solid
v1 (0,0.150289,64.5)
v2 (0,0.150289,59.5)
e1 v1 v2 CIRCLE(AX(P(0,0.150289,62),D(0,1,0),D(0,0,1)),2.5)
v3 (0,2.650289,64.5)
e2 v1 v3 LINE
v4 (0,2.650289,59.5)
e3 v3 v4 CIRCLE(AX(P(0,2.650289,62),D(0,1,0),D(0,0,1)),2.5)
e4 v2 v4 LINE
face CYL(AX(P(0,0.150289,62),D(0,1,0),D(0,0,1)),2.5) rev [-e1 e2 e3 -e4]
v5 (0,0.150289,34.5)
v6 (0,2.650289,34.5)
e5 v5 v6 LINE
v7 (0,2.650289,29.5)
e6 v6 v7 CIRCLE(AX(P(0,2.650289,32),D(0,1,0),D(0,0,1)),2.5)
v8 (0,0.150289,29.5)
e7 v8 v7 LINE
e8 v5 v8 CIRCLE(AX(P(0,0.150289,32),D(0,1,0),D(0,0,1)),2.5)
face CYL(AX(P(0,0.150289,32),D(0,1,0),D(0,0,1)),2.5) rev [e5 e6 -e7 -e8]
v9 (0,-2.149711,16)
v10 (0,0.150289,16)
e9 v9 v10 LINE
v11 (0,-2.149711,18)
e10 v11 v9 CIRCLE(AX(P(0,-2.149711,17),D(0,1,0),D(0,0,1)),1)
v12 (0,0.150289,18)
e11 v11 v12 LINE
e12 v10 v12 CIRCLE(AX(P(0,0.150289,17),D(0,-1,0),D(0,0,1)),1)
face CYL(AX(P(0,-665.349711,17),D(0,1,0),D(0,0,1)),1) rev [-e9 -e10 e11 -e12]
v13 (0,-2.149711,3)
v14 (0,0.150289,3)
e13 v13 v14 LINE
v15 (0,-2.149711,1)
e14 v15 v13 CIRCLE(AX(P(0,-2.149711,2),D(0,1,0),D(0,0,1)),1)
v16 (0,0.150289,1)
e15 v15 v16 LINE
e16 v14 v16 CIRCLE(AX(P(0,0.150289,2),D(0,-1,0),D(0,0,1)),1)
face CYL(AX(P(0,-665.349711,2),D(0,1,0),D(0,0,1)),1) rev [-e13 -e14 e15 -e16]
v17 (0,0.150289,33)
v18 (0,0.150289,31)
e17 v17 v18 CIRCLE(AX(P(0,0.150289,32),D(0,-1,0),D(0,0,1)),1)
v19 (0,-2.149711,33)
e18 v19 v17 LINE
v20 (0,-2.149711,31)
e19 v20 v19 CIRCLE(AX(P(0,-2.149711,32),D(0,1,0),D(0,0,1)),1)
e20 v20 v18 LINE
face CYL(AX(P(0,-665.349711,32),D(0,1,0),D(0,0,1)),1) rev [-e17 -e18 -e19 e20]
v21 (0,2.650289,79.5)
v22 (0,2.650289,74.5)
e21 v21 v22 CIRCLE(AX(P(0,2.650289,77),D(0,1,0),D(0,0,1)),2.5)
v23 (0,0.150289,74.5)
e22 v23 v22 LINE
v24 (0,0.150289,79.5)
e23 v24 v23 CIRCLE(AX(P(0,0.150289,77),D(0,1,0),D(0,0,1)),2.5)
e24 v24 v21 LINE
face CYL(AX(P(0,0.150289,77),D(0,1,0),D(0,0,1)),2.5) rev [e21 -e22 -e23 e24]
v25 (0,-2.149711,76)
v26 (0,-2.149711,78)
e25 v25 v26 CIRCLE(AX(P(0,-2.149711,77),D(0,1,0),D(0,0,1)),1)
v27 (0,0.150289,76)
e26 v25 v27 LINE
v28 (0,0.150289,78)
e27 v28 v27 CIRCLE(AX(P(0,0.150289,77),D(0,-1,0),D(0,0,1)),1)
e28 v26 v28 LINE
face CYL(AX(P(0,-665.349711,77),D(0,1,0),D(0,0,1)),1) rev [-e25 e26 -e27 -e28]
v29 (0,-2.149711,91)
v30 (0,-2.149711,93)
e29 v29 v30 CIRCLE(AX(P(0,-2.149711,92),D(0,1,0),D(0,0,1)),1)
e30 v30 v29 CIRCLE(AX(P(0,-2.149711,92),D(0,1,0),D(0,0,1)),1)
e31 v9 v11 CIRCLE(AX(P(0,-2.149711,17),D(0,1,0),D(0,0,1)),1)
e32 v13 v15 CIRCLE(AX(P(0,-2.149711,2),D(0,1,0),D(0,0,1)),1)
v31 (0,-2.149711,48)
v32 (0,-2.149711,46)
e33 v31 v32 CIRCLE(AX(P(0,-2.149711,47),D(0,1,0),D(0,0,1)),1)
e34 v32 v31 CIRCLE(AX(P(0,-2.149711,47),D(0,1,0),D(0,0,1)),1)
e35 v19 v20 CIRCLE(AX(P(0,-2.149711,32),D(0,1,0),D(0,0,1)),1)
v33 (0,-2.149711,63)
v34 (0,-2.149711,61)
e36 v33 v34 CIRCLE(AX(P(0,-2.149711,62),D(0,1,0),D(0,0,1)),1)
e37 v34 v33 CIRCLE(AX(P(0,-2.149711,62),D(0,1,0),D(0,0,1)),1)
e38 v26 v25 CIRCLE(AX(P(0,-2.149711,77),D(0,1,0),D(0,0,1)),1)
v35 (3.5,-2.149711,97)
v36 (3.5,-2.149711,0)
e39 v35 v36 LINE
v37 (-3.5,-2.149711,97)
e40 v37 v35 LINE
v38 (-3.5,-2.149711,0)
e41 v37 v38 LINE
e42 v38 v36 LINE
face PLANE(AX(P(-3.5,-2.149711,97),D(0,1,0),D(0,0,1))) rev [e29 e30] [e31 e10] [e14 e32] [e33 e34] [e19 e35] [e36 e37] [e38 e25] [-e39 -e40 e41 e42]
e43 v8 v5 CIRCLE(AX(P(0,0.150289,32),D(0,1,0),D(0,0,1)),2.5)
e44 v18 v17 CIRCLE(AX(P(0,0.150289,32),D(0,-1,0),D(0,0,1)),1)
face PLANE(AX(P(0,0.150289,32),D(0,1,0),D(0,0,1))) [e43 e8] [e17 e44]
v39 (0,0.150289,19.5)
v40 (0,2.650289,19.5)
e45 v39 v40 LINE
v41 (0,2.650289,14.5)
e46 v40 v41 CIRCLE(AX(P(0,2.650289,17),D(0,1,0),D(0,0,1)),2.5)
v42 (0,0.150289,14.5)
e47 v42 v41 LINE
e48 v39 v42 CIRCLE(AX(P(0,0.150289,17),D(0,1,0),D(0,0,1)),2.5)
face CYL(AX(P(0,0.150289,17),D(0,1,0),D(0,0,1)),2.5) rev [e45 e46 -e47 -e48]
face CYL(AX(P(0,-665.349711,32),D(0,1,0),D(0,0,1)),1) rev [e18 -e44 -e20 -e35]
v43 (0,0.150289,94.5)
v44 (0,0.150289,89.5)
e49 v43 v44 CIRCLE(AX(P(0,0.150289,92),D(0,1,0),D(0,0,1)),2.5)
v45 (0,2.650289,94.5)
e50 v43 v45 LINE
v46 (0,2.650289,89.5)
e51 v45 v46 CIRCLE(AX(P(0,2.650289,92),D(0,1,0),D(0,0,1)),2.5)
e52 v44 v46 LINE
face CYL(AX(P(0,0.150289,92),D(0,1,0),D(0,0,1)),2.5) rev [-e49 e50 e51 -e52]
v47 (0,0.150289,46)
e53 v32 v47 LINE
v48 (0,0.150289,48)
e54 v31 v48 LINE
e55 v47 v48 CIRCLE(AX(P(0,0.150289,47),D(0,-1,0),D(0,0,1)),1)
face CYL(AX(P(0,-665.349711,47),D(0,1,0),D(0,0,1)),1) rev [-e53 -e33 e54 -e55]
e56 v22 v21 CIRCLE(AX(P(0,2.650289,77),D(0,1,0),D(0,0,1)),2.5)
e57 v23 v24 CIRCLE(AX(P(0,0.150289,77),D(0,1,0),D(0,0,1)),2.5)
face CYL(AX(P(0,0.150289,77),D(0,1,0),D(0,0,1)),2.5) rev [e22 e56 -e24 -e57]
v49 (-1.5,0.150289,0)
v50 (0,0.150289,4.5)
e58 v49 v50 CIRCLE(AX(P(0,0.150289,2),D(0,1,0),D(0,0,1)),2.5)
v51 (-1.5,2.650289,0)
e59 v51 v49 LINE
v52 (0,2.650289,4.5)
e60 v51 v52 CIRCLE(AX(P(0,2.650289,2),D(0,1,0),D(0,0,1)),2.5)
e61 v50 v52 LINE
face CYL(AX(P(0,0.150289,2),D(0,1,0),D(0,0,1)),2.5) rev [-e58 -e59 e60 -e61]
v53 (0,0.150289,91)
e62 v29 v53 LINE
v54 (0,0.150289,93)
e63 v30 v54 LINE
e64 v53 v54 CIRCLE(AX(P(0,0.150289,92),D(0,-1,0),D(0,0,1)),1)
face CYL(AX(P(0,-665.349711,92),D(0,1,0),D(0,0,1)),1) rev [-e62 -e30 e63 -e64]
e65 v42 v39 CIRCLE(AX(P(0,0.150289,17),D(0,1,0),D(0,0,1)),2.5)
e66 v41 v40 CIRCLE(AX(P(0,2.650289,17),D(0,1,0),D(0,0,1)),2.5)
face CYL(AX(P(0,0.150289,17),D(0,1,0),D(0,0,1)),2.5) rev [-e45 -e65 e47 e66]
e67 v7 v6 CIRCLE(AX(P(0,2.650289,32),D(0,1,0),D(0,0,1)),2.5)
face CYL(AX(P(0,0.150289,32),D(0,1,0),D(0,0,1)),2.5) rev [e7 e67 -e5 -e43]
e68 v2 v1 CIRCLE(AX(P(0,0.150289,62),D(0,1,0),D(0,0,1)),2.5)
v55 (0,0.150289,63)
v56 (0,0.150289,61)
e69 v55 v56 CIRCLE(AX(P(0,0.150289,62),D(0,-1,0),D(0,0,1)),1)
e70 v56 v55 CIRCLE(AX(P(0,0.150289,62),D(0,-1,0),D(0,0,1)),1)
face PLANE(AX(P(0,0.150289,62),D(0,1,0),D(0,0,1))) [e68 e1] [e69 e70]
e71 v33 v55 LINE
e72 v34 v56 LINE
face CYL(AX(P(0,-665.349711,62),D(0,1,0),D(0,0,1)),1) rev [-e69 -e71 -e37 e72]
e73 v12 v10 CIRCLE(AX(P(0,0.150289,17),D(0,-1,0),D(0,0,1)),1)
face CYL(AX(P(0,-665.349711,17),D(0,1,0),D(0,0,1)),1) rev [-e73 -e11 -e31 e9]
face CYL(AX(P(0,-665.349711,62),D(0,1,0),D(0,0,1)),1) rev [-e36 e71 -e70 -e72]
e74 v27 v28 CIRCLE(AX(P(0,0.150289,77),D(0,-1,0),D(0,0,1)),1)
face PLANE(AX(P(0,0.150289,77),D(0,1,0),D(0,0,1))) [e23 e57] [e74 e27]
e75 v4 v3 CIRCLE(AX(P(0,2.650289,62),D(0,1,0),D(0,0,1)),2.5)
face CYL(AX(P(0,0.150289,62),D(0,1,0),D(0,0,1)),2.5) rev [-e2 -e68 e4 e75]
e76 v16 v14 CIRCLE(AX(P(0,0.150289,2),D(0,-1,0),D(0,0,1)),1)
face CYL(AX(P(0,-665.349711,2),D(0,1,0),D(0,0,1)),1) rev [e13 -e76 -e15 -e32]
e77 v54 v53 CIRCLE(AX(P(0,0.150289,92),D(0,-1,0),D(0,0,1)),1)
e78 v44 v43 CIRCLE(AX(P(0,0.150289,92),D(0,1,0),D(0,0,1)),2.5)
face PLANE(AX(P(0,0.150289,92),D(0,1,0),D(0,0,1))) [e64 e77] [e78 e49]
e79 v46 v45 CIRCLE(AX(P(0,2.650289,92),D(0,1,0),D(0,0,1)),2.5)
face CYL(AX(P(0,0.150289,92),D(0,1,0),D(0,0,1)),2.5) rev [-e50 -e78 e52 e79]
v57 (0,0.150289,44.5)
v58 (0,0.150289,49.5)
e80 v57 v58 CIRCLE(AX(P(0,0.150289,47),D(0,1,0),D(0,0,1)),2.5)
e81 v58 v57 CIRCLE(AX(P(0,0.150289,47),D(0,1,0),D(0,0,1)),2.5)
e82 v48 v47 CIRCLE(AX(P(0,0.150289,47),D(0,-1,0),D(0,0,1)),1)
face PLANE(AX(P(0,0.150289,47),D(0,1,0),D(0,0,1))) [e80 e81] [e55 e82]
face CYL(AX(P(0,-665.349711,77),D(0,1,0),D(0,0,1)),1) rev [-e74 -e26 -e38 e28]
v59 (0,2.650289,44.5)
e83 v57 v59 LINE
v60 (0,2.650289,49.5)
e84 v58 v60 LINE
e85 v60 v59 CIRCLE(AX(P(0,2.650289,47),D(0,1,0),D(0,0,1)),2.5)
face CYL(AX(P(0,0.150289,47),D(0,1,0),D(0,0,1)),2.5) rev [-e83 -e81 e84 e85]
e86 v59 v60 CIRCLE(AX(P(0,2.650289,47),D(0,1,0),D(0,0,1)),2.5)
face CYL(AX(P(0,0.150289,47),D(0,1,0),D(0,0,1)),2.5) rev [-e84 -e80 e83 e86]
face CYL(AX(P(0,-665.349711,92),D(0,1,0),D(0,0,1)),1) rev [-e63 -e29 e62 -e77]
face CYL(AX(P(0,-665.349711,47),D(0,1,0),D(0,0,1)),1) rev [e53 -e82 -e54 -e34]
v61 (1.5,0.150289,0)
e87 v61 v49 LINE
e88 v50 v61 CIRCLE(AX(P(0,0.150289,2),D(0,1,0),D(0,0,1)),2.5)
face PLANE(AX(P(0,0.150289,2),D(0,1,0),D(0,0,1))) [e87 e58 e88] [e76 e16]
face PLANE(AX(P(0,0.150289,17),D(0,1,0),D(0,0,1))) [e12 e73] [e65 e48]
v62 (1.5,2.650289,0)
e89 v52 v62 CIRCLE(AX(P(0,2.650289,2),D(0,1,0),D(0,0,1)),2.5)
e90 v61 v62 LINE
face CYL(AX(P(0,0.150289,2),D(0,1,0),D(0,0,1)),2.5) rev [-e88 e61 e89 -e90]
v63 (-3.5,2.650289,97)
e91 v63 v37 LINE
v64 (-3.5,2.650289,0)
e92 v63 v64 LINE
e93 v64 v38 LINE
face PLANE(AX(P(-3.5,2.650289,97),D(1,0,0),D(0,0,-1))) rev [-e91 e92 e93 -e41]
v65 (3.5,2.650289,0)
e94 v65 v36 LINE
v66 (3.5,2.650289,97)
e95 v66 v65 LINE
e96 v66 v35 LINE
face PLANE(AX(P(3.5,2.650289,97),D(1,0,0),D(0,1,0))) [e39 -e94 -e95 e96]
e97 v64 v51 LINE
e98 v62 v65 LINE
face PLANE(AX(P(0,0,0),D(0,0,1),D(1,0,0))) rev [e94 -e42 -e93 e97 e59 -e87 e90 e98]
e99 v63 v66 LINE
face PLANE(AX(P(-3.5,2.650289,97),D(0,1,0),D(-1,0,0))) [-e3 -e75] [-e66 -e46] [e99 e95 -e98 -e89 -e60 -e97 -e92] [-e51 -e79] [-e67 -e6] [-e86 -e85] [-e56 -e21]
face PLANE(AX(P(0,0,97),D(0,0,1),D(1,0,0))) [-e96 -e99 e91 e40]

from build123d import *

# Parameters (mm, degrees)
SKETCH1_W           = 7
SKETCH1_H           = 4.8
BOSS_EXTRUDE1_DEPTH = 97
SKETCH2_R           = 1
CUT_EXTRUDE1_DEPTH  = 668
SKETCH3_R           = 2.5
CUT_EXTRUDE2_DEPTH  = 2.5
LPATTERN1_COUNT     = 7
LPATTERN1_PITCH     = 15


with BuildPart() as part:
    # Sketch1 → Boss-Extrude1 (new body)
    with BuildSketch(Plane.XY):
        with Locations((0, 0.250289017)):
            Rectangle(SKETCH1_W, SKETCH1_H)
    extrude(amount=BOSS_EXTRUDE1_DEPTH)

    # Sketch2 → Cut-Extrude1 (cut)
    with BuildSketch(Plane(origin=(0, 2.650289017, 0), x_dir=(1, 0, 0), z_dir=(0, 1, 0))):
        with Locations(Location((0, -92, 0), (0, 0, 270))):
            Circle(SKETCH2_R)
    cut_extrude1 = extrude(amount=-CUT_EXTRUDE1_DEPTH, mode=Mode.SUBTRACT)

    # Sketch3 → Cut-Extrude2 (cut)
    with BuildSketch(Plane(origin=(0, 2.650289017, 0), x_dir=(1, 0, 0), z_dir=(0, 1, 0))):
        with Locations(Location((0, -92, 0), (0, 0, 270))):
            Circle(SKETCH3_R)
    cut_extrude2 = extrude(amount=-CUT_EXTRUDE2_DEPTH, mode=Mode.SUBTRACT)

    # LPattern1: Cut-Extrude1, Cut-Extrude2 ×7
    with Locations(*[(0, 0, -i * LPATTERN1_PITCH) for i in range(1, LPATTERN1_COUNT)]):
        add(cut_extrude1, mode=Mode.SUBTRACT)
        add(cut_extrude2, mode=Mode.SUBTRACT)


solid = part.part
